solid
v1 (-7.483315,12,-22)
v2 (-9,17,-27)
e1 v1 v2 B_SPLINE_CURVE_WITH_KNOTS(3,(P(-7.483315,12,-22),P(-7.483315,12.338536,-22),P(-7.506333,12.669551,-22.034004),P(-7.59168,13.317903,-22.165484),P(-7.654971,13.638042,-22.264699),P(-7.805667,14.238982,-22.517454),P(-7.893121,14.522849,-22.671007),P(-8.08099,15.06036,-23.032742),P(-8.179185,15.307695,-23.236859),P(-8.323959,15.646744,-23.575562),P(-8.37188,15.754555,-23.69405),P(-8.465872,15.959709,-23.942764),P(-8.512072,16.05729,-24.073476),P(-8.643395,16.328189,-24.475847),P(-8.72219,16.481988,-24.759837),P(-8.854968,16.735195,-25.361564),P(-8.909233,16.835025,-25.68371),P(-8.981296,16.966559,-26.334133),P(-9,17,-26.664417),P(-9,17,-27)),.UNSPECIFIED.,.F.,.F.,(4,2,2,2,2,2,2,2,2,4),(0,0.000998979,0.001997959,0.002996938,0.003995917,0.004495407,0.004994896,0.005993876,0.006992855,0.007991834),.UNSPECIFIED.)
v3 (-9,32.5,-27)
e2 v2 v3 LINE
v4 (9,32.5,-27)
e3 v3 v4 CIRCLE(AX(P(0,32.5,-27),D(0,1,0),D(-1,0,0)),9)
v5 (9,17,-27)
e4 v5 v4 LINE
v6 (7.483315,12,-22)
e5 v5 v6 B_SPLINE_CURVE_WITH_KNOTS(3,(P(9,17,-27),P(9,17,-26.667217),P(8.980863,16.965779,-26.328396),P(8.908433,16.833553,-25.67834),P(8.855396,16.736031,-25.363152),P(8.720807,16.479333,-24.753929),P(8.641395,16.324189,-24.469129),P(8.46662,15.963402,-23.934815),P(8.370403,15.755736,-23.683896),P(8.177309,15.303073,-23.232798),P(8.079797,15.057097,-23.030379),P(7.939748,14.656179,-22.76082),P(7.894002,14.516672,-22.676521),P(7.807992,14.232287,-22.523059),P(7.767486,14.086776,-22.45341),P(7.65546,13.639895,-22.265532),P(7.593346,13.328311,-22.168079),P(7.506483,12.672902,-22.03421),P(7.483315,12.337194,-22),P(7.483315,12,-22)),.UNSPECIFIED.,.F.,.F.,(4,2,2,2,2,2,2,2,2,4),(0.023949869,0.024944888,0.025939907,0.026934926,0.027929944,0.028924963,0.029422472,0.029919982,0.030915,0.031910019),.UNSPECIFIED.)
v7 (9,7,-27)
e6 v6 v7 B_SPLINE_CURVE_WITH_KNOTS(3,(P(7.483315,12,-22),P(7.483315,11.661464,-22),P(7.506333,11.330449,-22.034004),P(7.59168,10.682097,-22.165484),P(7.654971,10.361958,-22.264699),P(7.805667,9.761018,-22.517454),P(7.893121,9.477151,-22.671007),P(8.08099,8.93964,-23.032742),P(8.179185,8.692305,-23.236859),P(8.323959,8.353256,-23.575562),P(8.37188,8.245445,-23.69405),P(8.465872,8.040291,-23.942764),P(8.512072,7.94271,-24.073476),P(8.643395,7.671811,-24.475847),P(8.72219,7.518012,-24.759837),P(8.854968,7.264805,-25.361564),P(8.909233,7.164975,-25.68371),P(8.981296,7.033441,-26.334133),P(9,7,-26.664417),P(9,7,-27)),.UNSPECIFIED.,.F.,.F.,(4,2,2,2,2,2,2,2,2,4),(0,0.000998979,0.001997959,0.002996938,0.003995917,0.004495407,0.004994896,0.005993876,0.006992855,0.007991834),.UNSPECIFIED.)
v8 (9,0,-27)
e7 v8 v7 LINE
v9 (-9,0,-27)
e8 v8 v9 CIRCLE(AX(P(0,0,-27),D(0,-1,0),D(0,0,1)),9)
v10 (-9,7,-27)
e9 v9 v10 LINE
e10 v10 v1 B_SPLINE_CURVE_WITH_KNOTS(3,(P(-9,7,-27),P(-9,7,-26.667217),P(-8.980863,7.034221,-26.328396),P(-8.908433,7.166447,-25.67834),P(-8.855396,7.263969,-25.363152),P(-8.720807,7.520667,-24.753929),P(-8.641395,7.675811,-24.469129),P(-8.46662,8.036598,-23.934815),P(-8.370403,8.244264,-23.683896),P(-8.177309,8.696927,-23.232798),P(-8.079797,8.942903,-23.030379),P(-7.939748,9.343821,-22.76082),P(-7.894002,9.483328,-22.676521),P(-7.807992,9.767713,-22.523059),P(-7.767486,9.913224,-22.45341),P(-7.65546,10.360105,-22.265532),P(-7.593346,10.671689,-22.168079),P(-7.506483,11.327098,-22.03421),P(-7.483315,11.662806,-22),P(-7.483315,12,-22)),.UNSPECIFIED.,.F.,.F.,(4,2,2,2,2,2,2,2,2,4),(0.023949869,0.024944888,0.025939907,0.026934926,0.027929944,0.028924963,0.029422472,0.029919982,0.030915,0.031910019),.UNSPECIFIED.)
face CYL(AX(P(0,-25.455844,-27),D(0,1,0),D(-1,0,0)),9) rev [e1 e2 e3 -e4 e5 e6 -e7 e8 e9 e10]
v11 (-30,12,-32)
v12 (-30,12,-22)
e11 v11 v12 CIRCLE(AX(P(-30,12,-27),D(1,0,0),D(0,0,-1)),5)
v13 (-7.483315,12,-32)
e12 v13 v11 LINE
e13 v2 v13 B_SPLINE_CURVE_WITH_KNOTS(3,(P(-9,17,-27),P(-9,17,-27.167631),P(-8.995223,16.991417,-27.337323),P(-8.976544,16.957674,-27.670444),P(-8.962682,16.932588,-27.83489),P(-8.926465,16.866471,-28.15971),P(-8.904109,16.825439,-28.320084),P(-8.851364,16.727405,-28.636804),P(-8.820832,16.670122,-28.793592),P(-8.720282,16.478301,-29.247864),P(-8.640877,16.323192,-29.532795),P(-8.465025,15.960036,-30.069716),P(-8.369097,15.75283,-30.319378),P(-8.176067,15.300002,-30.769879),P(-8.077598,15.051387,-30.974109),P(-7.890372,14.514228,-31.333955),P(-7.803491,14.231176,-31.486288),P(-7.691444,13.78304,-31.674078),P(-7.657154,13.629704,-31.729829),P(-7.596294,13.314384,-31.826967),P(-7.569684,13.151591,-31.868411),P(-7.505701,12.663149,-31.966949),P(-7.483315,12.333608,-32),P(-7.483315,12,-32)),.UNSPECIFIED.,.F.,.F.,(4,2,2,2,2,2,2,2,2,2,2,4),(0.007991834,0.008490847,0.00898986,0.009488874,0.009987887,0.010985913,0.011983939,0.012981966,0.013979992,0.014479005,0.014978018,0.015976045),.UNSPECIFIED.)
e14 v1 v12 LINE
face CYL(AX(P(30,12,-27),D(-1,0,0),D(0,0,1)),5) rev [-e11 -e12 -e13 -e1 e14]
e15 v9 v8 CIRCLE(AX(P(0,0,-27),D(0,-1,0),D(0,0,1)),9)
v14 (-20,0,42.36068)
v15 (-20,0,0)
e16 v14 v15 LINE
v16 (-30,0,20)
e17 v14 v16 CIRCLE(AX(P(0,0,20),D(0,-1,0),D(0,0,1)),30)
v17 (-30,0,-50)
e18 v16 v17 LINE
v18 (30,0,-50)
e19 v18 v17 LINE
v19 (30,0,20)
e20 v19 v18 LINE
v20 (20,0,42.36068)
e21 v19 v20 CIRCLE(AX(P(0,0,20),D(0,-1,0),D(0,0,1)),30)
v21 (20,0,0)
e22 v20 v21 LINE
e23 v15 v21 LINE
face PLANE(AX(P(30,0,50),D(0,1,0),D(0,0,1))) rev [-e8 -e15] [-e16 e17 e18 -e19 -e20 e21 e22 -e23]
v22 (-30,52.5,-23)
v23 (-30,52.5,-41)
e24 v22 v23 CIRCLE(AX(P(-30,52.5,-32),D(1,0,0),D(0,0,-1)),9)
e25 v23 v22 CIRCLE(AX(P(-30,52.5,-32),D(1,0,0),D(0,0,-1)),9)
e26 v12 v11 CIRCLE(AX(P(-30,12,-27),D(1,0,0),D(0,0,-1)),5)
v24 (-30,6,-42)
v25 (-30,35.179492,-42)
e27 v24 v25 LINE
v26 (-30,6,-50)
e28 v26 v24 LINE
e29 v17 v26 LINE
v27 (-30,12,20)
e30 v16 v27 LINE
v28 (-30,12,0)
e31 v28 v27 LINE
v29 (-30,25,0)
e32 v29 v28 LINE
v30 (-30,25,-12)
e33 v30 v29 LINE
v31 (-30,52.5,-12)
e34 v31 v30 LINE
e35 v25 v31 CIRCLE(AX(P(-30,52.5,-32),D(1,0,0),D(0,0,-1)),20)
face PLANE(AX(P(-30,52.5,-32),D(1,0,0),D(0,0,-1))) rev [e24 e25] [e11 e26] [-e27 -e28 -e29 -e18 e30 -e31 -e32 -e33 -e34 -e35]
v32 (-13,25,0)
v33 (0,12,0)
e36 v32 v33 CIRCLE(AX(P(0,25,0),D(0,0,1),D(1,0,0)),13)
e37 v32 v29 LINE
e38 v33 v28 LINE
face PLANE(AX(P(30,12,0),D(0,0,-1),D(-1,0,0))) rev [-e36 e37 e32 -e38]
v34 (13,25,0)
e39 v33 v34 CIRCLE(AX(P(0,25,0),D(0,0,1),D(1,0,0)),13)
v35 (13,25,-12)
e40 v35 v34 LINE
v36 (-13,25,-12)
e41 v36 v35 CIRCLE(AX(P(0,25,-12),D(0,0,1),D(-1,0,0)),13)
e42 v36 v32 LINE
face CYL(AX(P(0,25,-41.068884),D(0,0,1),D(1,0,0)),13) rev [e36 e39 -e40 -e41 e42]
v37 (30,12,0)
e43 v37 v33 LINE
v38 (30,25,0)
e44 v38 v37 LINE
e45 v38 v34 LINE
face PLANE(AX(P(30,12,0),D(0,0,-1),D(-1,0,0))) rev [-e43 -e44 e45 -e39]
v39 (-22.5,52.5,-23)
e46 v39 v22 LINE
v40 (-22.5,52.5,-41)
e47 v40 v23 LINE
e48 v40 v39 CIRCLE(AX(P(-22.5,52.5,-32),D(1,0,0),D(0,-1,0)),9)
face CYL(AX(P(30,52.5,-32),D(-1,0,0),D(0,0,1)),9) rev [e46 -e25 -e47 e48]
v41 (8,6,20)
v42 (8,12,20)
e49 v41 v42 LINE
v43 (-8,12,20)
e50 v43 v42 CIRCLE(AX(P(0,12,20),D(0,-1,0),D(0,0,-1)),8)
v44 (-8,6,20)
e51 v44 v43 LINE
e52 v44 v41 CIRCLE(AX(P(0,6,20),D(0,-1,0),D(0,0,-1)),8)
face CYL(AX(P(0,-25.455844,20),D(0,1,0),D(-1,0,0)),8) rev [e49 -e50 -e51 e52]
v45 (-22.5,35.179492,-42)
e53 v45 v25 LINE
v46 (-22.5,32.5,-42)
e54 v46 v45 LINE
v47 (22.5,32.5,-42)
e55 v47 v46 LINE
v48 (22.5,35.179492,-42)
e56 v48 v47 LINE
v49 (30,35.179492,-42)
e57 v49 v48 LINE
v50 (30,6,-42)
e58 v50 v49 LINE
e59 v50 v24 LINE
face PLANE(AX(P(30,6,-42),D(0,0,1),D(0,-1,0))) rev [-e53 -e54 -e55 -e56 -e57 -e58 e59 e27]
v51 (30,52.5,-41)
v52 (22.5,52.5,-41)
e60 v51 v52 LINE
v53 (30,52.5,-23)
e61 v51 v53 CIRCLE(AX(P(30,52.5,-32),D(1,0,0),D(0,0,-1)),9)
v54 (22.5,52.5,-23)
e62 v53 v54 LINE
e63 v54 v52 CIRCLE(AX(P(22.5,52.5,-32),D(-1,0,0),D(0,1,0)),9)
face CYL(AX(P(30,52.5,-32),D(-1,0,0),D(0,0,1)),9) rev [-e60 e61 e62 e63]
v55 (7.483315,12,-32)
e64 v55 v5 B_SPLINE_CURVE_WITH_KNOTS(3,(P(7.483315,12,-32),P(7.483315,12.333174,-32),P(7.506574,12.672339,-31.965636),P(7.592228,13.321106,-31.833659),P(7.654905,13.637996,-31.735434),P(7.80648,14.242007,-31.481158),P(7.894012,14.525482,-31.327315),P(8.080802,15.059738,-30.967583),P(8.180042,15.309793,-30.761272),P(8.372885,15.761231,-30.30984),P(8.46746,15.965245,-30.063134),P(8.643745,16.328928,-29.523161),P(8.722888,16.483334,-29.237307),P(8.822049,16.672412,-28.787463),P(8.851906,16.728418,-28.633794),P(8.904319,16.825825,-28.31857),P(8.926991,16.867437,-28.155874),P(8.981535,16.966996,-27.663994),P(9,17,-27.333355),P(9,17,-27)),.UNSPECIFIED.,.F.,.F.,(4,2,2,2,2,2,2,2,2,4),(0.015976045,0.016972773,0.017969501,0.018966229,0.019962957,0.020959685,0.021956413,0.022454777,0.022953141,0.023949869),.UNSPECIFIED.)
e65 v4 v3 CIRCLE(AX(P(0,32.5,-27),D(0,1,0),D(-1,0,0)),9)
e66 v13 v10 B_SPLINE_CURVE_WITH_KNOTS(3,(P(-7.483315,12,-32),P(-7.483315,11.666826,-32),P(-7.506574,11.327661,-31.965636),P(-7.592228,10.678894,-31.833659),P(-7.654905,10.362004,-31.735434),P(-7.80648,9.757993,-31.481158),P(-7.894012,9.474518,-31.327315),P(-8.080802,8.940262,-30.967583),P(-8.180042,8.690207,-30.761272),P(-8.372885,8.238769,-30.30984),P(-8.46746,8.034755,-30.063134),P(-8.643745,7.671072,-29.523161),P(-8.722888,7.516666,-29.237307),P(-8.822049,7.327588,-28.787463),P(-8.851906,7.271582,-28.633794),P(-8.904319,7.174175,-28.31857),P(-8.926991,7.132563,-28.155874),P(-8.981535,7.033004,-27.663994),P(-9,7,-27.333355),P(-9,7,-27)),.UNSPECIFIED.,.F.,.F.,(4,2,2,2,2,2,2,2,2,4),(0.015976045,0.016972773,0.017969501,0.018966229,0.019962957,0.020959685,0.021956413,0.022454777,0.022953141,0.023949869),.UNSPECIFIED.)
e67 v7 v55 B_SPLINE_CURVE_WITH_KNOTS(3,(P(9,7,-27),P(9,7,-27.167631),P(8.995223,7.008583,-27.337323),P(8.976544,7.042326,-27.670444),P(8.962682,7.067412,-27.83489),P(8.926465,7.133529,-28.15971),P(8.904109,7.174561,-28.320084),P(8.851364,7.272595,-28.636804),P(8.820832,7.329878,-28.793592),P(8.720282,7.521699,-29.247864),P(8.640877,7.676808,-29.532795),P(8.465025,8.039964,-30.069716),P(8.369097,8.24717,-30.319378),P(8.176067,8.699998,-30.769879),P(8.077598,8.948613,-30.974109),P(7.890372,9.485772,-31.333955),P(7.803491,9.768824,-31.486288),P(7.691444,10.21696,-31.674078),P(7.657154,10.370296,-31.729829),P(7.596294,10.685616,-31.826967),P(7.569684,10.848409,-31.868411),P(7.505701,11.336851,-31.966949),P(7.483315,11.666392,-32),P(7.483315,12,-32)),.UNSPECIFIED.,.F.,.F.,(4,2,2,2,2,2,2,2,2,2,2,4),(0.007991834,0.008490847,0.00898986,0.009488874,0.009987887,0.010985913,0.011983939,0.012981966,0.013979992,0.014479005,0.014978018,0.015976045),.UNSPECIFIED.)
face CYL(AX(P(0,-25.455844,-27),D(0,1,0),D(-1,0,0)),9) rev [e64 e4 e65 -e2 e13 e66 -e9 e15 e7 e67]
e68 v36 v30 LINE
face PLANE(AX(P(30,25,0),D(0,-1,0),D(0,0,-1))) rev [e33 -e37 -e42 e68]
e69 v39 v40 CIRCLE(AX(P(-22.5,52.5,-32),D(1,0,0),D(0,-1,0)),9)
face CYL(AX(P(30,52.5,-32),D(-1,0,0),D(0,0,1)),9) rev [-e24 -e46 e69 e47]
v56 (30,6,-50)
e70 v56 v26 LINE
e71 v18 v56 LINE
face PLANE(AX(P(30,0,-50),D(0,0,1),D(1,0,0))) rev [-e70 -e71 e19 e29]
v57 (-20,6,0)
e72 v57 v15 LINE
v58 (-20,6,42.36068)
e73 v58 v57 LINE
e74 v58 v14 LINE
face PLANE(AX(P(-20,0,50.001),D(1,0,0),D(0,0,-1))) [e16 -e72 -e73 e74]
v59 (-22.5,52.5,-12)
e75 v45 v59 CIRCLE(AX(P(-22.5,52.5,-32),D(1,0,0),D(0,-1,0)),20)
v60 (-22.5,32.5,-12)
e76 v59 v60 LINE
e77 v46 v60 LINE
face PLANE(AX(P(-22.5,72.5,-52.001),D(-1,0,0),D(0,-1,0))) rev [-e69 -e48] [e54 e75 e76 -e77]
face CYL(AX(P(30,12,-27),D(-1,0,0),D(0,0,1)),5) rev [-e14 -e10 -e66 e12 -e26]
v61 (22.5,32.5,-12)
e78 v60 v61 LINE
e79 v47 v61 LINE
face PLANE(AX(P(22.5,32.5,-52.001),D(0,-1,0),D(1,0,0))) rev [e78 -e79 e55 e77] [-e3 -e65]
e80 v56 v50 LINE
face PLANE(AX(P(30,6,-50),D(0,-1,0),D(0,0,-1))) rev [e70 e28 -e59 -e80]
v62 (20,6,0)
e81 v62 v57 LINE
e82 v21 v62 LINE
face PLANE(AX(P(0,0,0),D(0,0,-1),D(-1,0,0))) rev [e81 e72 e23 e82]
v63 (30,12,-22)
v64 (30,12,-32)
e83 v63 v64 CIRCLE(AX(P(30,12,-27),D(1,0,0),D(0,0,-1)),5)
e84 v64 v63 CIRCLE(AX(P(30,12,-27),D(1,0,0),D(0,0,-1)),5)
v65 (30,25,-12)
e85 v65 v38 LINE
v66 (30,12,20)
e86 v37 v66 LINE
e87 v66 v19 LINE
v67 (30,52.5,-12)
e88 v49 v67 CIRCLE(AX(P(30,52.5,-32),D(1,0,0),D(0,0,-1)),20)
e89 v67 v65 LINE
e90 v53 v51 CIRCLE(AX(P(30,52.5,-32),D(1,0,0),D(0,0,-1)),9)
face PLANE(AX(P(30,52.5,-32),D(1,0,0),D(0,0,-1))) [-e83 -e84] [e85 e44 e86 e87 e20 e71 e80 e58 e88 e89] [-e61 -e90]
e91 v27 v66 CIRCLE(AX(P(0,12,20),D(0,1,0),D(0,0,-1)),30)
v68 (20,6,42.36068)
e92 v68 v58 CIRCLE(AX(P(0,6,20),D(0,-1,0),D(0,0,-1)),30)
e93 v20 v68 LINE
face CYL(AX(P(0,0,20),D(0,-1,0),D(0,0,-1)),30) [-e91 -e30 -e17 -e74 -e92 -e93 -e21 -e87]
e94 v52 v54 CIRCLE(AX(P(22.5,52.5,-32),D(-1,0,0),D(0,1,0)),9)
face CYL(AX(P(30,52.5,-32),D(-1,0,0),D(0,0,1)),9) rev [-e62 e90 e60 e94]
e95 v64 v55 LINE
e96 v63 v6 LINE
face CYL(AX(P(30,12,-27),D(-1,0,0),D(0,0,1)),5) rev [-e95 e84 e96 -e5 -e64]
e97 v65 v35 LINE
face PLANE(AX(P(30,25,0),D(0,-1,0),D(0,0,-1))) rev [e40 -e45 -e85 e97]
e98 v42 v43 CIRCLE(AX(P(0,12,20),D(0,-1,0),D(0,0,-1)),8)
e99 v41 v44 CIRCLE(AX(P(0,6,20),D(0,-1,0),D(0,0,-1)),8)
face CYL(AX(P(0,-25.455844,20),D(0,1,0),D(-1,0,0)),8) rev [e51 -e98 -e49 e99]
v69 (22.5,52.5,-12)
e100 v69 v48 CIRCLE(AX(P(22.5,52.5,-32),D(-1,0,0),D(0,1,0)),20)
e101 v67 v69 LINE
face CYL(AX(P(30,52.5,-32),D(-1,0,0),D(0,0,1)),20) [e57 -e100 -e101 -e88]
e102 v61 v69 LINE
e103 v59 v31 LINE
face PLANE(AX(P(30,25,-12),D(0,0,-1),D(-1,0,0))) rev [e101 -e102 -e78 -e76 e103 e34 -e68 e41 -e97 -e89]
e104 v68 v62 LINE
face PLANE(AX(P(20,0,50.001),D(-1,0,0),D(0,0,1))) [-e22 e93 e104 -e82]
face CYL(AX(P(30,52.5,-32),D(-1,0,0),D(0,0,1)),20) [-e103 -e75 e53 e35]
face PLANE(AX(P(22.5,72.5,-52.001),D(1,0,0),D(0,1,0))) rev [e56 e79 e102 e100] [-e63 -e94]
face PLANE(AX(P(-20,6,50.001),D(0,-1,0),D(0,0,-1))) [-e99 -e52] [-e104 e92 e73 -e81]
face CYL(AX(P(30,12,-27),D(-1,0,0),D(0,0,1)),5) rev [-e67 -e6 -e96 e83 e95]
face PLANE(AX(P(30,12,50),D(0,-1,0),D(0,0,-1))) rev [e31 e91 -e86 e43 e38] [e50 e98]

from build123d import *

# Parameters (mm, degrees)
BRACKET_SIDE_PROFILE_SKETCH_R    = 9
BRACKET_SIDE_PROFILE_SKETCH_R_2  = 5
BRACKET_BODY_60MM_DEPTH          = 30
BODY_FILLETS_RADIUS              = 30
BODY_FILLETS_LENGTH              = 12
BORE_13_DEPTH                    = 12
CLEVIS_SLOT_REACH                = 102.001
CLEVIS_SLOT_SKETCH_W             = 45
CLEVIS_SLOT_SKETCH_H             = 40
SADDLE_CUT_REACH                 = 74.139
SADDLE_CUT_SKETCH_R              = 9
SADDLE_CUT_SKETCH_R_2            = 8
BASE_UNDERSIDE_RELIEF_REACH      = 96.129
BASE_UNDERSIDE_RELIEF_END_RADIUS = 30
BASE_UNDERSIDE_RELIEF_SKETCH_W   = 40
BASE_UNDERSIDE_RELIEF_SKETCH_H   = 6


with BuildPart() as part:
    # Bracket Side Profile Sketch → Bracket Body 60mm (new, symmetric)
    with BuildSketch(Plane(origin=(0, 0, 0), x_dir=(0, 0, -1), z_dir=(1, 0, 0))):
        with BuildLine():
            Line((0, 12), (0, 25))
            Line((0, 25), (12, 25))
            Line((12, 25), (12, 52.5))
            ThreePointArc((12, 52.5), (42, 69.820508076), (42, 35.179491924))
            Line((42, 35.179491924), (42, 6))
            Line((42, 6), (50, 6))
            Line((50, 6), (50, 0))
            Line((50, 0), (-50, 0))
            Line((-50, 0), (-50, 12))
            Line((-50, 12), (0, 12))
        make_face()
        with Locations((32, 52.5)):
            Circle(BRACKET_SIDE_PROFILE_SKETCH_R, mode=Mode.SUBTRACT)
        with Locations((27, 12)):
            Circle(BRACKET_SIDE_PROFILE_SKETCH_R_2, mode=Mode.SUBTRACT)
    extrude(amount=BRACKET_BODY_60MM_DEPTH, both=True)

    # Body Fillets: full round fillet: the end face becomes a half cylinder, R = half its width
    body_fillets_face = Plane((0, 6, 50), x_dir=(0, -1, 0), z_dir=(0, 0, 1))  # on the end face: x along it, z out of the body
    body_fillets_slab = body_fillets_face.offset(-BODY_FILLETS_RADIUS / 2) * Box(BODY_FILLETS_LENGTH, 2 * BODY_FILLETS_RADIUS, BODY_FILLETS_RADIUS, mode=Mode.PRIVATE)  # the body's end, R deep
    body_fillets_round = Plane((0, 6, 20), x_dir=(0, 0, 1), z_dir=(0, -1, 0)) * Cylinder(BODY_FILLETS_RADIUS, BODY_FILLETS_LENGTH, mode=Mode.PRIVATE)  # its axis R under the face
    add(body_fillets_slab - body_fillets_round, mode=Mode.SUBTRACT)

    # Bore _13 Sketch → Bore _13 (cut)
    with BuildSketch(Plane.XY):
        with BuildLine():
            Line((-13, 25), (13, 25))
            ThreePointArc((13, 25), (0, 12), (-13, 25))
        make_face()
    extrude(amount=-BORE_13_DEPTH, mode=Mode.SUBTRACT)

    # Clevis Slot Sketch → Clevis Slot (cut, up to next)
    with BuildSketch(Plane.XY.offset(-12), mode=Mode.PRIVATE) as clevis_slot_sk1:
        with Locations((0, 52.5)):
            Rectangle(CLEVIS_SLOT_SKETCH_W, CLEVIS_SLOT_SKETCH_H)
    clevis_slot_tool1 = extrude(clevis_slot_sk1.sketch, amount=-CLEVIS_SLOT_REACH, mode=Mode.PRIVATE) & part.part
    add(clevis_slot_tool1.solids().sort_by_distance((0, 52.5, -12))[0], mode=Mode.SUBTRACT)

    # Saddle Cut: up to this face of the body (flat: up to its plane)
    saddle_cut_end = Plane(part.part.faces().sort_by_distance((0, 0, -2.979428252))[0])
    # Saddle Cut Sketch → Saddle Cut (cut, up to the picked face)
    with BuildSketch(Plane(origin=(0, 32.5, 0), x_dir=(1, 0, 0), z_dir=(0, 1, 0)), mode=Mode.PRIVATE) as saddle_cut_sk1:
        with Locations(Location((0, 27, 0), (0, 0, 180))):
            Circle(SADDLE_CUT_SKETCH_R)
    saddle_cut_tool1 = split(extrude(saddle_cut_sk1.sketch, amount=-SADDLE_CUT_REACH, mode=Mode.PRIVATE), bisect_by=saddle_cut_end, keep=Keep.BOTH, mode=Mode.PRIVATE)
    # Saddle Cut Sketch → Saddle Cut (cut, up to the picked face)
    with BuildSketch(Plane(origin=(0, 32.5, 0), x_dir=(1, 0, 0), z_dir=(0, 1, 0)), mode=Mode.PRIVATE) as saddle_cut_sk2:
        with Locations(Location((0, -20, 0), (0, 0, 270))):
            Circle(SADDLE_CUT_SKETCH_R_2)
    saddle_cut_tool2 = split(extrude(saddle_cut_sk2.sketch, amount=-SADDLE_CUT_REACH, mode=Mode.PRIVATE), bisect_by=saddle_cut_end, keep=Keep.BOTH, mode=Mode.PRIVATE)
    add(saddle_cut_tool1.solids().sort_by(Axis((0, 32.5, -27), (0, -1, 0)))[0], mode=Mode.SUBTRACT)
    add(saddle_cut_tool2.solids().sort_by(Axis((0, 32.5, 20), (0, -1, 0)))[0], mode=Mode.SUBTRACT)

    # Base Underside Relief: up to this cylinder (the profile starts inside it)
    base_underside_relief_end = Plane(origin=(0, 3, 20), z_dir=(0, -1, 0)) * Cylinder(BASE_UNDERSIDE_RELIEF_END_RADIUS, 253.258, mode=Mode.PRIVATE)
    # Base Underside Relief Sketch → Base Underside Relief (cut, up to the surface)
    with BuildSketch(Plane.XY, mode=Mode.PRIVATE) as base_underside_relief_sk1:
        with Locations((0, 3)):
            Rectangle(BASE_UNDERSIDE_RELIEF_SKETCH_W, BASE_UNDERSIDE_RELIEF_SKETCH_H)
    base_underside_relief_tool1 = extrude(base_underside_relief_sk1.sketch, amount=BASE_UNDERSIDE_RELIEF_REACH, mode=Mode.PRIVATE) & base_underside_relief_end
    add(base_underside_relief_tool1.solids().sort_by_distance((0, 3, 0))[0], mode=Mode.SUBTRACT)


solid = part.part
